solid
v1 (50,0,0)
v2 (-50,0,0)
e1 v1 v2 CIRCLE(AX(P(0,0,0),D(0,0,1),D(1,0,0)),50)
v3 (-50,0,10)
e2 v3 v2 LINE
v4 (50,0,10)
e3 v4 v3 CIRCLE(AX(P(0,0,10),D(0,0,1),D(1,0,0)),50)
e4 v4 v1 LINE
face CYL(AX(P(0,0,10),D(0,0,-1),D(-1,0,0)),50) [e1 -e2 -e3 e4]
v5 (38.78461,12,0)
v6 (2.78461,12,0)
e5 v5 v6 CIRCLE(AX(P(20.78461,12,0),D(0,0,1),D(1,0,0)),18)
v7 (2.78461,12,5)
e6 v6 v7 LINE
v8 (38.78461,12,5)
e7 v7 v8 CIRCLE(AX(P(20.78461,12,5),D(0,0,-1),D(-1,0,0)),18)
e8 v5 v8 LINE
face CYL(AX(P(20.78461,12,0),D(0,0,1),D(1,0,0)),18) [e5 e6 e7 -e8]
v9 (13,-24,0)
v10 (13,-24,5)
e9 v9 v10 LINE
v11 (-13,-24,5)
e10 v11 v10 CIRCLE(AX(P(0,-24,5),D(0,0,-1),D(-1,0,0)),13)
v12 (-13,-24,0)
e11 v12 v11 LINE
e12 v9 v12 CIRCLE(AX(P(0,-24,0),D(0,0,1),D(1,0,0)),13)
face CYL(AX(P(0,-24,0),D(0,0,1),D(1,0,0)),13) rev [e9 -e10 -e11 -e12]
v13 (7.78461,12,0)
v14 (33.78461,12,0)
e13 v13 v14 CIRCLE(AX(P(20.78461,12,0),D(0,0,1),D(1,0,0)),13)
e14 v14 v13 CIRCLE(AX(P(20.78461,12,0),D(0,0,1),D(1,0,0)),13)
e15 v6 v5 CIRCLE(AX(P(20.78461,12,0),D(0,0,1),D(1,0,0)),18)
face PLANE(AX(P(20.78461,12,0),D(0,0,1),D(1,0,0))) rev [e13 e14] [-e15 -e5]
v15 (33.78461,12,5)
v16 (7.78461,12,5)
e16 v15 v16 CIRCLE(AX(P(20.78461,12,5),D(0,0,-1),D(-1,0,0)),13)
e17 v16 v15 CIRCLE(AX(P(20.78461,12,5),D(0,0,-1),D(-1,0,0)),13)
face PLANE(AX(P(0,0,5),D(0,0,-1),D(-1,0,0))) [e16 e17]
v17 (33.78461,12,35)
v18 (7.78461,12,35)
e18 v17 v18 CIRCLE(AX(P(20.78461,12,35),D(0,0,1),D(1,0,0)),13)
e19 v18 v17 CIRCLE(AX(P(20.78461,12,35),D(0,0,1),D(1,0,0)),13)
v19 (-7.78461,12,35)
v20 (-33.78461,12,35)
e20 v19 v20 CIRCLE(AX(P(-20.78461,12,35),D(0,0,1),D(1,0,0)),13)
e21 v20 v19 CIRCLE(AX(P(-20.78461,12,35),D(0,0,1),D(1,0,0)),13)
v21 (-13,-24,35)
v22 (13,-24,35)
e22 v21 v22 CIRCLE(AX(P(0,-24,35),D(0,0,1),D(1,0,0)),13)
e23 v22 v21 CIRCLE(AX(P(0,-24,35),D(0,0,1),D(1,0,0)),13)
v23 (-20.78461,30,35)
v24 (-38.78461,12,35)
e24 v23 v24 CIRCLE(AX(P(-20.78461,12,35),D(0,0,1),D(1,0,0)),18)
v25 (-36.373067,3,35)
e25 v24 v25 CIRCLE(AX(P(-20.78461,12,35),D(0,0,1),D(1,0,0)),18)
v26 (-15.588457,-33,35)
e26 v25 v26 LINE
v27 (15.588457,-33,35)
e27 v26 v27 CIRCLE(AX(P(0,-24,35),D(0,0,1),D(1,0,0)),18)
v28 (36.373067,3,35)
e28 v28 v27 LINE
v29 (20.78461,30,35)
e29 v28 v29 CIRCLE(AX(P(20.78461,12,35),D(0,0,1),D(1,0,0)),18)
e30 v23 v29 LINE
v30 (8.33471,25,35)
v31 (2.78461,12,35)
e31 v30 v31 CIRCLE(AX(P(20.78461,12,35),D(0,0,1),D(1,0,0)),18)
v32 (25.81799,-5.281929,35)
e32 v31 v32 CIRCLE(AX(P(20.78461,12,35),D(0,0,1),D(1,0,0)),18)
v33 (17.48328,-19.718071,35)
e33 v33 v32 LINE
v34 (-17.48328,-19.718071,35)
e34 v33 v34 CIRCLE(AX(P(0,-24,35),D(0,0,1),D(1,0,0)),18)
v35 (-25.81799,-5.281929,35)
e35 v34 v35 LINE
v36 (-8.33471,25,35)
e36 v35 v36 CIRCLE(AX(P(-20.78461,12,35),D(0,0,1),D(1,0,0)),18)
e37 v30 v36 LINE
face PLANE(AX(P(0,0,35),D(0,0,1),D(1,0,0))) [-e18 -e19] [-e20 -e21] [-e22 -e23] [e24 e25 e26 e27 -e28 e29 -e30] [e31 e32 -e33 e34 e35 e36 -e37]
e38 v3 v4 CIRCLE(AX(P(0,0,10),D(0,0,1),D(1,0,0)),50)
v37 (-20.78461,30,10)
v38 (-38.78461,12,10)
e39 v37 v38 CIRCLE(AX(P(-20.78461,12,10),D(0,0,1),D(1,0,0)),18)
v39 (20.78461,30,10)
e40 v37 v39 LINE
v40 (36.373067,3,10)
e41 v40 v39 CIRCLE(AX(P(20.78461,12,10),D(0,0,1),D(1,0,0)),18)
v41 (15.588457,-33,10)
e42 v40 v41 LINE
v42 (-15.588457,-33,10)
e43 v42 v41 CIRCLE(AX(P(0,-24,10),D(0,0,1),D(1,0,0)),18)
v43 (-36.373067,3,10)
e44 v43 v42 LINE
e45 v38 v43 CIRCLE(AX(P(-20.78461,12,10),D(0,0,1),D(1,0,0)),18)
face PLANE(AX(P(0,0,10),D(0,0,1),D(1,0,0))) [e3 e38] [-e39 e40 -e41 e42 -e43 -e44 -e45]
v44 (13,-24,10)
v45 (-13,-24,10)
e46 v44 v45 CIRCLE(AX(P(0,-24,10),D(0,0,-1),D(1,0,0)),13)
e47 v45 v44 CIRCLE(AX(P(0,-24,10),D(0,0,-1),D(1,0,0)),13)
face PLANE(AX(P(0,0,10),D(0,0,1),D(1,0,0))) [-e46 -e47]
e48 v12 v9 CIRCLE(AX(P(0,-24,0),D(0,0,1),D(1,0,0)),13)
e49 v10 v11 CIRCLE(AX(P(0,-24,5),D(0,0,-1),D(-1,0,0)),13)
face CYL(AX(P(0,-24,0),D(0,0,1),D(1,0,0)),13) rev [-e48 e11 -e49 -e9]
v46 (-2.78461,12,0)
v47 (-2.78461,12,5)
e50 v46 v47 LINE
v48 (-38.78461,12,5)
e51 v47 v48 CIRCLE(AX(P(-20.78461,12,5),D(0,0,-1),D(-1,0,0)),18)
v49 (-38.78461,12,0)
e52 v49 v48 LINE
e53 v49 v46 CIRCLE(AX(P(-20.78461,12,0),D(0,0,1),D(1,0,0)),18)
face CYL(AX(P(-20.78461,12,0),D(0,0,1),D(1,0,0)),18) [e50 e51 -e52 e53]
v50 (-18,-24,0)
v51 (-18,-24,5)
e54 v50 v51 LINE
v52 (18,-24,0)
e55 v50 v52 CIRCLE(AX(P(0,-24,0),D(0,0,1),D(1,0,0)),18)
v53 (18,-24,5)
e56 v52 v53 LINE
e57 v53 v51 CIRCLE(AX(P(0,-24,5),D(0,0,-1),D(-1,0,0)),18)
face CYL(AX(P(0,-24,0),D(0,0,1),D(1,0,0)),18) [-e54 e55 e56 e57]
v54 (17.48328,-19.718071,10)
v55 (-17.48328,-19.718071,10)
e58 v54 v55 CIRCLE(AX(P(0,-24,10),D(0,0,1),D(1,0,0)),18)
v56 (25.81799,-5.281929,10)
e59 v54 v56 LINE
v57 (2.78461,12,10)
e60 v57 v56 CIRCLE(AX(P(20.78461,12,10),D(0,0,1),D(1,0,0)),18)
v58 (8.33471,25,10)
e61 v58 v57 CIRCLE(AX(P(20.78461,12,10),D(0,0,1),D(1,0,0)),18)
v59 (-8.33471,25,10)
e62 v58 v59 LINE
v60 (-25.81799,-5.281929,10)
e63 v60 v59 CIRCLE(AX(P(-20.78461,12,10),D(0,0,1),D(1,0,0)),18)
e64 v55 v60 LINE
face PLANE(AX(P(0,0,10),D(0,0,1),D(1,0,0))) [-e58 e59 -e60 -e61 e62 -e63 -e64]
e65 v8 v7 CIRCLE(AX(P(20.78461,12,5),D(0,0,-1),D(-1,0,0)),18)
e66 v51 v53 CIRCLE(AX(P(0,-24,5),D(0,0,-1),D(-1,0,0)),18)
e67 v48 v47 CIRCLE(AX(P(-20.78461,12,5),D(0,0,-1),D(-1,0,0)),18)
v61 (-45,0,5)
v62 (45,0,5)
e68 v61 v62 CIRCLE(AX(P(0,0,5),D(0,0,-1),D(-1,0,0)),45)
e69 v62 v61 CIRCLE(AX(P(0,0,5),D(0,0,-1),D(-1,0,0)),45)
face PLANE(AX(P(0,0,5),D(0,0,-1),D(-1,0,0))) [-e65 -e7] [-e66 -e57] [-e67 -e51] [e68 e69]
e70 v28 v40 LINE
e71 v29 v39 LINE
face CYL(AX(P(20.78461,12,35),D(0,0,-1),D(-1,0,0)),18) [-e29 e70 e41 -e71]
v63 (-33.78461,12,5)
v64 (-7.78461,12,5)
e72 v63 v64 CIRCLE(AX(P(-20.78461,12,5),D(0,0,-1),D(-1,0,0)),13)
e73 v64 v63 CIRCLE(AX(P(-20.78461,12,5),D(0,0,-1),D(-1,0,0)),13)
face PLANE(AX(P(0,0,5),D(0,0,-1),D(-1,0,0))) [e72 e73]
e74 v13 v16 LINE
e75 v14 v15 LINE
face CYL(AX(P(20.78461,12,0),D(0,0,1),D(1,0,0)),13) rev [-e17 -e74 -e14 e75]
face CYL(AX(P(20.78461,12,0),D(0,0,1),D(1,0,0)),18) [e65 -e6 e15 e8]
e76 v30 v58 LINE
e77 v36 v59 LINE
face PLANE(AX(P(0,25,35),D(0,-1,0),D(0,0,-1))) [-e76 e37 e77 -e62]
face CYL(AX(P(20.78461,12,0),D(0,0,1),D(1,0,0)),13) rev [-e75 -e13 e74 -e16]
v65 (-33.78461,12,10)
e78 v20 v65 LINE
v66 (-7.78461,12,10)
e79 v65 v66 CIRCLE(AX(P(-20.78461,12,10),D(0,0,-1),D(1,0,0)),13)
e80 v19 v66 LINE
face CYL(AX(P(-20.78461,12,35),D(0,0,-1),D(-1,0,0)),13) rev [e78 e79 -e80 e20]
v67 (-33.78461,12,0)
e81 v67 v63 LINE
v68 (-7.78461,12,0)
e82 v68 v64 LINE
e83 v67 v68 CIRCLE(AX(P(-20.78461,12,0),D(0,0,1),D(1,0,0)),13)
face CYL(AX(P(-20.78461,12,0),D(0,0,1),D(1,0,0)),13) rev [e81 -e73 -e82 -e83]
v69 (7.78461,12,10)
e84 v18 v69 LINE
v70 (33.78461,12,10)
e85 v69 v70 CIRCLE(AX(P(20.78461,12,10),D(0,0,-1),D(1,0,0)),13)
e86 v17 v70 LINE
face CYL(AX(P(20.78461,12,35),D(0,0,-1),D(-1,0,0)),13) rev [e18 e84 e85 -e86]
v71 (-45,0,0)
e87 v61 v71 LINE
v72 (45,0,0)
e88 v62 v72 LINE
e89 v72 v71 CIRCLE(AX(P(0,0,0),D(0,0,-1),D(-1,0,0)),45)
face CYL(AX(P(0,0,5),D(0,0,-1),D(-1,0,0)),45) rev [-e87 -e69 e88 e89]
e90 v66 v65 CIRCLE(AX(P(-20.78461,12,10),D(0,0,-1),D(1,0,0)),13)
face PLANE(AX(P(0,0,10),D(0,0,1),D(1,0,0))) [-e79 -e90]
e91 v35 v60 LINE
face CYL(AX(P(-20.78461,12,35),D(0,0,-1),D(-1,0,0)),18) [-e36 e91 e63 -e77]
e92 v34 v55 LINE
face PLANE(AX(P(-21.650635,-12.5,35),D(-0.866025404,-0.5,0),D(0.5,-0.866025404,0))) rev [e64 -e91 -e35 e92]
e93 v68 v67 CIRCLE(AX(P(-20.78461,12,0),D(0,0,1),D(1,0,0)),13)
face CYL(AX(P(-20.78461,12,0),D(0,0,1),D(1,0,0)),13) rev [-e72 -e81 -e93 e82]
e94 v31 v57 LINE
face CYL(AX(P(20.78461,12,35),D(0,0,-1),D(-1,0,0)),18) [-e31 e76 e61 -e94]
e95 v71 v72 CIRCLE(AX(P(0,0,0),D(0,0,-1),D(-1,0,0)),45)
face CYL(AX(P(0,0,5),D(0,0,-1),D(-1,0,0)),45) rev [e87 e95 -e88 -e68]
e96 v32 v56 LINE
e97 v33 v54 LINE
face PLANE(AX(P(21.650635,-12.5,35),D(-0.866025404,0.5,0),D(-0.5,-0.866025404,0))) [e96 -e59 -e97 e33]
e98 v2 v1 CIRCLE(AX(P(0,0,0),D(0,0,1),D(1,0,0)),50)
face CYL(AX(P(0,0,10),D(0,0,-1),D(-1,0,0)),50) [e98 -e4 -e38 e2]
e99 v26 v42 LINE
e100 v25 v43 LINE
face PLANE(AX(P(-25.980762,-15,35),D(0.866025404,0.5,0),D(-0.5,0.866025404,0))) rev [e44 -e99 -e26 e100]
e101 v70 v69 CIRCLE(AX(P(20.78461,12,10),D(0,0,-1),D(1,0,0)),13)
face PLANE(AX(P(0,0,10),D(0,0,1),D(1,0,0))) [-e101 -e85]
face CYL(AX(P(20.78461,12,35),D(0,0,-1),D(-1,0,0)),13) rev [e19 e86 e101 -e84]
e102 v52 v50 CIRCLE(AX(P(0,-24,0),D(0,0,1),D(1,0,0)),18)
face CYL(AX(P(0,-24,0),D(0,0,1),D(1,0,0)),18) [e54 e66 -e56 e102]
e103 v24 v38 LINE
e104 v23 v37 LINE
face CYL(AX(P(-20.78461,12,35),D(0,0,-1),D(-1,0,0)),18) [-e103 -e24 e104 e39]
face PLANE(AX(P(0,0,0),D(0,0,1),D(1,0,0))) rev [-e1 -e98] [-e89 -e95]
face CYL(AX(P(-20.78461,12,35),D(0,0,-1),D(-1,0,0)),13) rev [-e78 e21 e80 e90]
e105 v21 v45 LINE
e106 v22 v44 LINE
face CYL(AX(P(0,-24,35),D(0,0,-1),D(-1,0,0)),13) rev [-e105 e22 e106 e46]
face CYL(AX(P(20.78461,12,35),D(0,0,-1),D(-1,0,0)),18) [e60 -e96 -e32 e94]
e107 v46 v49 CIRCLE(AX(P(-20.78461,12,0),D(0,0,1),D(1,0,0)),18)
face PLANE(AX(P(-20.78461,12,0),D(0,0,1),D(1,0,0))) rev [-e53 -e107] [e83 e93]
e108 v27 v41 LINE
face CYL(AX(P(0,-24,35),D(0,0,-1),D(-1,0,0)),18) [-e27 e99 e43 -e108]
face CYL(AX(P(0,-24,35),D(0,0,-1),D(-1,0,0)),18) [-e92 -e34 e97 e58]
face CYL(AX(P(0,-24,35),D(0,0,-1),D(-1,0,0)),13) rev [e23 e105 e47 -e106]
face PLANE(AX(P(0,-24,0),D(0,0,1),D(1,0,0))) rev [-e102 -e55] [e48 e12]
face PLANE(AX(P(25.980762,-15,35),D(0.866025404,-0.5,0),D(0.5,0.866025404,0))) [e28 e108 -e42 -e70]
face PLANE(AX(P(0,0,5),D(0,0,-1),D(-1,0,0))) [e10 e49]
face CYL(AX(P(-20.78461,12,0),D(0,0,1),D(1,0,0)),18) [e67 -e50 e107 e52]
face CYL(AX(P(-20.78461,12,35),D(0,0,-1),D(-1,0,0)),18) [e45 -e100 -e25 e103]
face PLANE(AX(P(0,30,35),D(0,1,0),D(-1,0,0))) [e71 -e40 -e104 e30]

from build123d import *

# Parameters (mm, degrees)
FLANGE_PROFILE_100_R       = 50
FLANGE_100X10_DEPTH        = 10
TUBE_CLUSTER_BOSS_DEPTH    = 25
FLANGE_RECESS_PROFILE_90_R = 45
FLANGE_RECESS_90X5_DEPTH   = 5
HOLLOW_START               = -35
TUBE_PROFILES_3X_36_26_R   = 18
TUBE_PROFILES_3X_36_26_R_2 = 13
HOLLOW_TUBES_3X_36_DEPTH   = 35


with BuildPart() as part:
    # Flange Profile Ø100 → Flange Ø100x10 (new body)
    with BuildSketch(Plane.XY):
        Circle(FLANGE_PROFILE_100_R)
    extrude(amount=FLANGE_100X10_DEPTH)

    # Tube Cluster Boss Profile → Tube Cluster Boss (add)
    with BuildSketch(Plane.XY.offset(10)):
        with BuildLine():
            ThreePointArc((-8.334710093, 25), (-14.076405758, 28.703293088), (-20.784609691, 30))
            ThreePointArc((-20.784609691, 30), (-36.373066959, 21), (-36.373066959, 3))
            ThreePointArc((-36.373066959, 3), (-31.895983866, -2.161121564), (-25.817990141, -5.281929326))
            ThreePointArc((-25.817990141, -5.281929326), (-15.830471874, -5.304812004), (-7.368201826, 0))
            Line((-7.368201826, 0), (-15.784609691, 0))
            ThreePointArc((-15.784609691, 0), (-31.601263517, 19.211102551), (-7.784609691, 12))
            ThreePointArc((-7.784609691, 12), (-8.227573949, 8.635352414), (-9.526279442, 5.5))
            Line((-9.526279442, 5.5), (-5.196152423, 3))
            ThreePointArc((-5.196152423, 3), (-3.397944818, 7.341257188), (-2.784609691, 12))
            ThreePointArc((-2.784609691, 12), (-4.23018139, 19.067595321), (-8.334710093, 25))
        make_face()
        with BuildLine():
            Line((-15.784609691, 0), (-7.368201826, 0))
            ThreePointArc((-7.368201826, 0), (-6.204810298, 1.443985143), (-5.196152423, 3))
            Line((-5.196152423, 3), (-9.526279442, 5.5))
            ThreePointArc((-9.526279442, 5.5), (-12.202895082, 2.235053795), (-15.784609691, 0))
        make_face()
        with BuildLine():
            ThreePointArc((-25.817990141, -5.281929326), (-31.895983866, -2.161121564), (-36.373066959, 3))
            Line((-36.373066959, 3), (-25.980762114, -15))
            Line((-25.980762114, -15), (-21.650635095, -12.5))
            Line((-21.650635095, -12.5), (-25.817990141, -5.281929326))
        make_face()
        with BuildLine():
            Line((-21.650635095, -12.5), (-25.980762114, -15))
            Line((-25.980762114, -15), (-15.588457268, -33))
            ThreePointArc((-15.588457268, -33), (-17.819578108, -26.542171525), (-17.483280048, -19.718070674))
            Line((-17.483280048, -19.718070674), (-21.650635095, -12.5))
        make_face()
        with BuildLine():
            ThreePointArc((17.483280048, -19.718070674), (11.111374175, -9.838878436), (0, -6))
            Line((0, -6), (0, -11))
            ThreePointArc((0, -11), (9.192388155, -14.807611845), (13, -24))
            ThreePointArc((13, -24), (9.192388155, -33.192388155), (0, -37))
            Line((0, -37), (0, -42))
            ThreePointArc((0, -42), (9, -39.588457268), (15.588457268, -33))
            ThreePointArc((15.588457268, -33), (17.386664873, -28.658742812), (18, -24))
            ThreePointArc((18, -24), (17.870353114, -21.843502941), (17.483280048, -19.718070674))
        make_face()
        with BuildLine():
            Line((0, -11), (0, -6))
            ThreePointArc((0, -6), (-11.111374175, -9.838878436), (-17.483280048, -19.718070674))
            ThreePointArc((-17.483280048, -19.718070674), (-17.819578108, -26.542171525), (-15.588457268, -33))
            ThreePointArc((-15.588457268, -33), (-9, -39.588457268), (0, -42))
            Line((0, -42), (0, -37))
            ThreePointArc((0, -37), (-13, -24), (0, -11))
        make_face()
        with BuildLine():
            Line((21.650635095, -12.5), (17.483280048, -19.718070674))
            ThreePointArc((17.483280048, -19.718070674), (17.870353114, -21.843502941), (18, -24))
            ThreePointArc((18, -24), (17.386664873, -28.658742812), (15.588457268, -33))
            Line((15.588457268, -33), (25.980762114, -15))
            Line((25.980762114, -15), (21.650635095, -12.5))
        make_face()
        with BuildLine():
            Line((25.980762114, -15), (36.373066959, 3))
            ThreePointArc((36.373066959, 3), (31.895983866, -2.161121564), (25.817990141, -5.281929326))
            Line((25.817990141, -5.281929326), (21.650635095, -12.5))
            Line((21.650635095, -12.5), (25.980762114, -15))
        make_face()
        with BuildLine():
            ThreePointArc((38.784609691, 12), (33.512531752, 24.727922061), (20.784609691, 30))
            ThreePointArc((20.784609691, 30), (14.076405758, 28.703293088), (8.334710093, 25))
            ThreePointArc((8.334710093, 25), (2.965031583, 14.542171525), (5.196152423, 3))
            Line((5.196152423, 3), (9.526279442, 5.5))
            ThreePointArc((9.526279442, 5.5), (17.419962104, 24.557035742), (33.784609691, 12))
            ThreePointArc((33.784609691, 12), (27.995712242, 1.183346174), (15.784609691, 0))
            Line((15.784609691, 0), (7.368201826, 0))
            ThreePointArc((7.368201826, 0), (15.830471874, -5.304812004), (25.817990141, -5.281929326))
            ThreePointArc((25.817990141, -5.281929326), (31.895983866, -2.161121564), (36.373066959, 3))
            ThreePointArc((36.373066959, 3), (38.171274564, 7.341257188), (38.784609691, 12))
        make_face()
        with BuildLine():
            Line((9.526279442, 5.5), (5.196152423, 3))
            ThreePointArc((5.196152423, 3), (6.204810298, 1.443985143), (7.368201826, 0))
            Line((7.368201826, 0), (15.784609691, 0))
            ThreePointArc((15.784609691, 0), (12.202895082, 2.235053795), (9.526279442, 5.5))
        make_face()
        with BuildLine():
            Line((20.784609691, 30), (0, 30))
            Line((0, 30), (0, 25))
            Line((0, 25), (8.334710093, 25))
            ThreePointArc((8.334710093, 25), (14.076405758, 28.703293088), (20.784609691, 30))
        make_face()
        with BuildLine():
            Line((0, 25), (0, 30))
            Line((0, 30), (-20.784609691, 30))
            ThreePointArc((-20.784609691, 30), (-14.076405758, 28.703293088), (-8.334710093, 25))
            Line((-8.334710093, 25), (0, 25))
        make_face()
    extrude(amount=TUBE_CLUSTER_BOSS_DEPTH)

    # Flange Recess Profile Ø90 → Flange Recess Ø90x5 (cut)
    with BuildSketch(Plane(origin=(0, 0, 0), x_dir=(-1, 0, 0), z_dir=(0, 0, -1))):
        Circle(FLANGE_RECESS_PROFILE_90_R)
    extrude(amount=-FLANGE_RECESS_90X5_DEPTH, mode=Mode.SUBTRACT)

    # Tube Profiles 3xØ36-Ø26 → Hollow Tubes 3xØ36 (add)
    # profile 1 of 3: a face of its own
    with BuildSketch(Plane.XY.offset(35).offset(HOLLOW_START)):
        with Locations((20.784609691, 12)):
            Circle(TUBE_PROFILES_3X_36_26_R)
        with Locations((20.784609691, 12)):
            Circle(TUBE_PROFILES_3X_36_26_R_2, mode=Mode.SUBTRACT)
    # profile 2 of 3: a face of its own
    with BuildSketch(Plane.XY.offset(35).offset(HOLLOW_START)):
        with Locations((-20.784609691, 12)):
            Circle(TUBE_PROFILES_3X_36_26_R)
        with Locations((-20.784609691, 12)):
            Circle(TUBE_PROFILES_3X_36_26_R_2, mode=Mode.SUBTRACT)
    # profile 3 of 3: a face of its own
    with BuildSketch(Plane.XY.offset(35).offset(HOLLOW_START)):
        with Locations((0, -24)):
            Circle(TUBE_PROFILES_3X_36_26_R)
        with Locations((0, -24)):
            Circle(TUBE_PROFILES_3X_36_26_R_2, mode=Mode.SUBTRACT)
    extrude(amount=HOLLOW_TUBES_3X_36_DEPTH)


solid = part.part
